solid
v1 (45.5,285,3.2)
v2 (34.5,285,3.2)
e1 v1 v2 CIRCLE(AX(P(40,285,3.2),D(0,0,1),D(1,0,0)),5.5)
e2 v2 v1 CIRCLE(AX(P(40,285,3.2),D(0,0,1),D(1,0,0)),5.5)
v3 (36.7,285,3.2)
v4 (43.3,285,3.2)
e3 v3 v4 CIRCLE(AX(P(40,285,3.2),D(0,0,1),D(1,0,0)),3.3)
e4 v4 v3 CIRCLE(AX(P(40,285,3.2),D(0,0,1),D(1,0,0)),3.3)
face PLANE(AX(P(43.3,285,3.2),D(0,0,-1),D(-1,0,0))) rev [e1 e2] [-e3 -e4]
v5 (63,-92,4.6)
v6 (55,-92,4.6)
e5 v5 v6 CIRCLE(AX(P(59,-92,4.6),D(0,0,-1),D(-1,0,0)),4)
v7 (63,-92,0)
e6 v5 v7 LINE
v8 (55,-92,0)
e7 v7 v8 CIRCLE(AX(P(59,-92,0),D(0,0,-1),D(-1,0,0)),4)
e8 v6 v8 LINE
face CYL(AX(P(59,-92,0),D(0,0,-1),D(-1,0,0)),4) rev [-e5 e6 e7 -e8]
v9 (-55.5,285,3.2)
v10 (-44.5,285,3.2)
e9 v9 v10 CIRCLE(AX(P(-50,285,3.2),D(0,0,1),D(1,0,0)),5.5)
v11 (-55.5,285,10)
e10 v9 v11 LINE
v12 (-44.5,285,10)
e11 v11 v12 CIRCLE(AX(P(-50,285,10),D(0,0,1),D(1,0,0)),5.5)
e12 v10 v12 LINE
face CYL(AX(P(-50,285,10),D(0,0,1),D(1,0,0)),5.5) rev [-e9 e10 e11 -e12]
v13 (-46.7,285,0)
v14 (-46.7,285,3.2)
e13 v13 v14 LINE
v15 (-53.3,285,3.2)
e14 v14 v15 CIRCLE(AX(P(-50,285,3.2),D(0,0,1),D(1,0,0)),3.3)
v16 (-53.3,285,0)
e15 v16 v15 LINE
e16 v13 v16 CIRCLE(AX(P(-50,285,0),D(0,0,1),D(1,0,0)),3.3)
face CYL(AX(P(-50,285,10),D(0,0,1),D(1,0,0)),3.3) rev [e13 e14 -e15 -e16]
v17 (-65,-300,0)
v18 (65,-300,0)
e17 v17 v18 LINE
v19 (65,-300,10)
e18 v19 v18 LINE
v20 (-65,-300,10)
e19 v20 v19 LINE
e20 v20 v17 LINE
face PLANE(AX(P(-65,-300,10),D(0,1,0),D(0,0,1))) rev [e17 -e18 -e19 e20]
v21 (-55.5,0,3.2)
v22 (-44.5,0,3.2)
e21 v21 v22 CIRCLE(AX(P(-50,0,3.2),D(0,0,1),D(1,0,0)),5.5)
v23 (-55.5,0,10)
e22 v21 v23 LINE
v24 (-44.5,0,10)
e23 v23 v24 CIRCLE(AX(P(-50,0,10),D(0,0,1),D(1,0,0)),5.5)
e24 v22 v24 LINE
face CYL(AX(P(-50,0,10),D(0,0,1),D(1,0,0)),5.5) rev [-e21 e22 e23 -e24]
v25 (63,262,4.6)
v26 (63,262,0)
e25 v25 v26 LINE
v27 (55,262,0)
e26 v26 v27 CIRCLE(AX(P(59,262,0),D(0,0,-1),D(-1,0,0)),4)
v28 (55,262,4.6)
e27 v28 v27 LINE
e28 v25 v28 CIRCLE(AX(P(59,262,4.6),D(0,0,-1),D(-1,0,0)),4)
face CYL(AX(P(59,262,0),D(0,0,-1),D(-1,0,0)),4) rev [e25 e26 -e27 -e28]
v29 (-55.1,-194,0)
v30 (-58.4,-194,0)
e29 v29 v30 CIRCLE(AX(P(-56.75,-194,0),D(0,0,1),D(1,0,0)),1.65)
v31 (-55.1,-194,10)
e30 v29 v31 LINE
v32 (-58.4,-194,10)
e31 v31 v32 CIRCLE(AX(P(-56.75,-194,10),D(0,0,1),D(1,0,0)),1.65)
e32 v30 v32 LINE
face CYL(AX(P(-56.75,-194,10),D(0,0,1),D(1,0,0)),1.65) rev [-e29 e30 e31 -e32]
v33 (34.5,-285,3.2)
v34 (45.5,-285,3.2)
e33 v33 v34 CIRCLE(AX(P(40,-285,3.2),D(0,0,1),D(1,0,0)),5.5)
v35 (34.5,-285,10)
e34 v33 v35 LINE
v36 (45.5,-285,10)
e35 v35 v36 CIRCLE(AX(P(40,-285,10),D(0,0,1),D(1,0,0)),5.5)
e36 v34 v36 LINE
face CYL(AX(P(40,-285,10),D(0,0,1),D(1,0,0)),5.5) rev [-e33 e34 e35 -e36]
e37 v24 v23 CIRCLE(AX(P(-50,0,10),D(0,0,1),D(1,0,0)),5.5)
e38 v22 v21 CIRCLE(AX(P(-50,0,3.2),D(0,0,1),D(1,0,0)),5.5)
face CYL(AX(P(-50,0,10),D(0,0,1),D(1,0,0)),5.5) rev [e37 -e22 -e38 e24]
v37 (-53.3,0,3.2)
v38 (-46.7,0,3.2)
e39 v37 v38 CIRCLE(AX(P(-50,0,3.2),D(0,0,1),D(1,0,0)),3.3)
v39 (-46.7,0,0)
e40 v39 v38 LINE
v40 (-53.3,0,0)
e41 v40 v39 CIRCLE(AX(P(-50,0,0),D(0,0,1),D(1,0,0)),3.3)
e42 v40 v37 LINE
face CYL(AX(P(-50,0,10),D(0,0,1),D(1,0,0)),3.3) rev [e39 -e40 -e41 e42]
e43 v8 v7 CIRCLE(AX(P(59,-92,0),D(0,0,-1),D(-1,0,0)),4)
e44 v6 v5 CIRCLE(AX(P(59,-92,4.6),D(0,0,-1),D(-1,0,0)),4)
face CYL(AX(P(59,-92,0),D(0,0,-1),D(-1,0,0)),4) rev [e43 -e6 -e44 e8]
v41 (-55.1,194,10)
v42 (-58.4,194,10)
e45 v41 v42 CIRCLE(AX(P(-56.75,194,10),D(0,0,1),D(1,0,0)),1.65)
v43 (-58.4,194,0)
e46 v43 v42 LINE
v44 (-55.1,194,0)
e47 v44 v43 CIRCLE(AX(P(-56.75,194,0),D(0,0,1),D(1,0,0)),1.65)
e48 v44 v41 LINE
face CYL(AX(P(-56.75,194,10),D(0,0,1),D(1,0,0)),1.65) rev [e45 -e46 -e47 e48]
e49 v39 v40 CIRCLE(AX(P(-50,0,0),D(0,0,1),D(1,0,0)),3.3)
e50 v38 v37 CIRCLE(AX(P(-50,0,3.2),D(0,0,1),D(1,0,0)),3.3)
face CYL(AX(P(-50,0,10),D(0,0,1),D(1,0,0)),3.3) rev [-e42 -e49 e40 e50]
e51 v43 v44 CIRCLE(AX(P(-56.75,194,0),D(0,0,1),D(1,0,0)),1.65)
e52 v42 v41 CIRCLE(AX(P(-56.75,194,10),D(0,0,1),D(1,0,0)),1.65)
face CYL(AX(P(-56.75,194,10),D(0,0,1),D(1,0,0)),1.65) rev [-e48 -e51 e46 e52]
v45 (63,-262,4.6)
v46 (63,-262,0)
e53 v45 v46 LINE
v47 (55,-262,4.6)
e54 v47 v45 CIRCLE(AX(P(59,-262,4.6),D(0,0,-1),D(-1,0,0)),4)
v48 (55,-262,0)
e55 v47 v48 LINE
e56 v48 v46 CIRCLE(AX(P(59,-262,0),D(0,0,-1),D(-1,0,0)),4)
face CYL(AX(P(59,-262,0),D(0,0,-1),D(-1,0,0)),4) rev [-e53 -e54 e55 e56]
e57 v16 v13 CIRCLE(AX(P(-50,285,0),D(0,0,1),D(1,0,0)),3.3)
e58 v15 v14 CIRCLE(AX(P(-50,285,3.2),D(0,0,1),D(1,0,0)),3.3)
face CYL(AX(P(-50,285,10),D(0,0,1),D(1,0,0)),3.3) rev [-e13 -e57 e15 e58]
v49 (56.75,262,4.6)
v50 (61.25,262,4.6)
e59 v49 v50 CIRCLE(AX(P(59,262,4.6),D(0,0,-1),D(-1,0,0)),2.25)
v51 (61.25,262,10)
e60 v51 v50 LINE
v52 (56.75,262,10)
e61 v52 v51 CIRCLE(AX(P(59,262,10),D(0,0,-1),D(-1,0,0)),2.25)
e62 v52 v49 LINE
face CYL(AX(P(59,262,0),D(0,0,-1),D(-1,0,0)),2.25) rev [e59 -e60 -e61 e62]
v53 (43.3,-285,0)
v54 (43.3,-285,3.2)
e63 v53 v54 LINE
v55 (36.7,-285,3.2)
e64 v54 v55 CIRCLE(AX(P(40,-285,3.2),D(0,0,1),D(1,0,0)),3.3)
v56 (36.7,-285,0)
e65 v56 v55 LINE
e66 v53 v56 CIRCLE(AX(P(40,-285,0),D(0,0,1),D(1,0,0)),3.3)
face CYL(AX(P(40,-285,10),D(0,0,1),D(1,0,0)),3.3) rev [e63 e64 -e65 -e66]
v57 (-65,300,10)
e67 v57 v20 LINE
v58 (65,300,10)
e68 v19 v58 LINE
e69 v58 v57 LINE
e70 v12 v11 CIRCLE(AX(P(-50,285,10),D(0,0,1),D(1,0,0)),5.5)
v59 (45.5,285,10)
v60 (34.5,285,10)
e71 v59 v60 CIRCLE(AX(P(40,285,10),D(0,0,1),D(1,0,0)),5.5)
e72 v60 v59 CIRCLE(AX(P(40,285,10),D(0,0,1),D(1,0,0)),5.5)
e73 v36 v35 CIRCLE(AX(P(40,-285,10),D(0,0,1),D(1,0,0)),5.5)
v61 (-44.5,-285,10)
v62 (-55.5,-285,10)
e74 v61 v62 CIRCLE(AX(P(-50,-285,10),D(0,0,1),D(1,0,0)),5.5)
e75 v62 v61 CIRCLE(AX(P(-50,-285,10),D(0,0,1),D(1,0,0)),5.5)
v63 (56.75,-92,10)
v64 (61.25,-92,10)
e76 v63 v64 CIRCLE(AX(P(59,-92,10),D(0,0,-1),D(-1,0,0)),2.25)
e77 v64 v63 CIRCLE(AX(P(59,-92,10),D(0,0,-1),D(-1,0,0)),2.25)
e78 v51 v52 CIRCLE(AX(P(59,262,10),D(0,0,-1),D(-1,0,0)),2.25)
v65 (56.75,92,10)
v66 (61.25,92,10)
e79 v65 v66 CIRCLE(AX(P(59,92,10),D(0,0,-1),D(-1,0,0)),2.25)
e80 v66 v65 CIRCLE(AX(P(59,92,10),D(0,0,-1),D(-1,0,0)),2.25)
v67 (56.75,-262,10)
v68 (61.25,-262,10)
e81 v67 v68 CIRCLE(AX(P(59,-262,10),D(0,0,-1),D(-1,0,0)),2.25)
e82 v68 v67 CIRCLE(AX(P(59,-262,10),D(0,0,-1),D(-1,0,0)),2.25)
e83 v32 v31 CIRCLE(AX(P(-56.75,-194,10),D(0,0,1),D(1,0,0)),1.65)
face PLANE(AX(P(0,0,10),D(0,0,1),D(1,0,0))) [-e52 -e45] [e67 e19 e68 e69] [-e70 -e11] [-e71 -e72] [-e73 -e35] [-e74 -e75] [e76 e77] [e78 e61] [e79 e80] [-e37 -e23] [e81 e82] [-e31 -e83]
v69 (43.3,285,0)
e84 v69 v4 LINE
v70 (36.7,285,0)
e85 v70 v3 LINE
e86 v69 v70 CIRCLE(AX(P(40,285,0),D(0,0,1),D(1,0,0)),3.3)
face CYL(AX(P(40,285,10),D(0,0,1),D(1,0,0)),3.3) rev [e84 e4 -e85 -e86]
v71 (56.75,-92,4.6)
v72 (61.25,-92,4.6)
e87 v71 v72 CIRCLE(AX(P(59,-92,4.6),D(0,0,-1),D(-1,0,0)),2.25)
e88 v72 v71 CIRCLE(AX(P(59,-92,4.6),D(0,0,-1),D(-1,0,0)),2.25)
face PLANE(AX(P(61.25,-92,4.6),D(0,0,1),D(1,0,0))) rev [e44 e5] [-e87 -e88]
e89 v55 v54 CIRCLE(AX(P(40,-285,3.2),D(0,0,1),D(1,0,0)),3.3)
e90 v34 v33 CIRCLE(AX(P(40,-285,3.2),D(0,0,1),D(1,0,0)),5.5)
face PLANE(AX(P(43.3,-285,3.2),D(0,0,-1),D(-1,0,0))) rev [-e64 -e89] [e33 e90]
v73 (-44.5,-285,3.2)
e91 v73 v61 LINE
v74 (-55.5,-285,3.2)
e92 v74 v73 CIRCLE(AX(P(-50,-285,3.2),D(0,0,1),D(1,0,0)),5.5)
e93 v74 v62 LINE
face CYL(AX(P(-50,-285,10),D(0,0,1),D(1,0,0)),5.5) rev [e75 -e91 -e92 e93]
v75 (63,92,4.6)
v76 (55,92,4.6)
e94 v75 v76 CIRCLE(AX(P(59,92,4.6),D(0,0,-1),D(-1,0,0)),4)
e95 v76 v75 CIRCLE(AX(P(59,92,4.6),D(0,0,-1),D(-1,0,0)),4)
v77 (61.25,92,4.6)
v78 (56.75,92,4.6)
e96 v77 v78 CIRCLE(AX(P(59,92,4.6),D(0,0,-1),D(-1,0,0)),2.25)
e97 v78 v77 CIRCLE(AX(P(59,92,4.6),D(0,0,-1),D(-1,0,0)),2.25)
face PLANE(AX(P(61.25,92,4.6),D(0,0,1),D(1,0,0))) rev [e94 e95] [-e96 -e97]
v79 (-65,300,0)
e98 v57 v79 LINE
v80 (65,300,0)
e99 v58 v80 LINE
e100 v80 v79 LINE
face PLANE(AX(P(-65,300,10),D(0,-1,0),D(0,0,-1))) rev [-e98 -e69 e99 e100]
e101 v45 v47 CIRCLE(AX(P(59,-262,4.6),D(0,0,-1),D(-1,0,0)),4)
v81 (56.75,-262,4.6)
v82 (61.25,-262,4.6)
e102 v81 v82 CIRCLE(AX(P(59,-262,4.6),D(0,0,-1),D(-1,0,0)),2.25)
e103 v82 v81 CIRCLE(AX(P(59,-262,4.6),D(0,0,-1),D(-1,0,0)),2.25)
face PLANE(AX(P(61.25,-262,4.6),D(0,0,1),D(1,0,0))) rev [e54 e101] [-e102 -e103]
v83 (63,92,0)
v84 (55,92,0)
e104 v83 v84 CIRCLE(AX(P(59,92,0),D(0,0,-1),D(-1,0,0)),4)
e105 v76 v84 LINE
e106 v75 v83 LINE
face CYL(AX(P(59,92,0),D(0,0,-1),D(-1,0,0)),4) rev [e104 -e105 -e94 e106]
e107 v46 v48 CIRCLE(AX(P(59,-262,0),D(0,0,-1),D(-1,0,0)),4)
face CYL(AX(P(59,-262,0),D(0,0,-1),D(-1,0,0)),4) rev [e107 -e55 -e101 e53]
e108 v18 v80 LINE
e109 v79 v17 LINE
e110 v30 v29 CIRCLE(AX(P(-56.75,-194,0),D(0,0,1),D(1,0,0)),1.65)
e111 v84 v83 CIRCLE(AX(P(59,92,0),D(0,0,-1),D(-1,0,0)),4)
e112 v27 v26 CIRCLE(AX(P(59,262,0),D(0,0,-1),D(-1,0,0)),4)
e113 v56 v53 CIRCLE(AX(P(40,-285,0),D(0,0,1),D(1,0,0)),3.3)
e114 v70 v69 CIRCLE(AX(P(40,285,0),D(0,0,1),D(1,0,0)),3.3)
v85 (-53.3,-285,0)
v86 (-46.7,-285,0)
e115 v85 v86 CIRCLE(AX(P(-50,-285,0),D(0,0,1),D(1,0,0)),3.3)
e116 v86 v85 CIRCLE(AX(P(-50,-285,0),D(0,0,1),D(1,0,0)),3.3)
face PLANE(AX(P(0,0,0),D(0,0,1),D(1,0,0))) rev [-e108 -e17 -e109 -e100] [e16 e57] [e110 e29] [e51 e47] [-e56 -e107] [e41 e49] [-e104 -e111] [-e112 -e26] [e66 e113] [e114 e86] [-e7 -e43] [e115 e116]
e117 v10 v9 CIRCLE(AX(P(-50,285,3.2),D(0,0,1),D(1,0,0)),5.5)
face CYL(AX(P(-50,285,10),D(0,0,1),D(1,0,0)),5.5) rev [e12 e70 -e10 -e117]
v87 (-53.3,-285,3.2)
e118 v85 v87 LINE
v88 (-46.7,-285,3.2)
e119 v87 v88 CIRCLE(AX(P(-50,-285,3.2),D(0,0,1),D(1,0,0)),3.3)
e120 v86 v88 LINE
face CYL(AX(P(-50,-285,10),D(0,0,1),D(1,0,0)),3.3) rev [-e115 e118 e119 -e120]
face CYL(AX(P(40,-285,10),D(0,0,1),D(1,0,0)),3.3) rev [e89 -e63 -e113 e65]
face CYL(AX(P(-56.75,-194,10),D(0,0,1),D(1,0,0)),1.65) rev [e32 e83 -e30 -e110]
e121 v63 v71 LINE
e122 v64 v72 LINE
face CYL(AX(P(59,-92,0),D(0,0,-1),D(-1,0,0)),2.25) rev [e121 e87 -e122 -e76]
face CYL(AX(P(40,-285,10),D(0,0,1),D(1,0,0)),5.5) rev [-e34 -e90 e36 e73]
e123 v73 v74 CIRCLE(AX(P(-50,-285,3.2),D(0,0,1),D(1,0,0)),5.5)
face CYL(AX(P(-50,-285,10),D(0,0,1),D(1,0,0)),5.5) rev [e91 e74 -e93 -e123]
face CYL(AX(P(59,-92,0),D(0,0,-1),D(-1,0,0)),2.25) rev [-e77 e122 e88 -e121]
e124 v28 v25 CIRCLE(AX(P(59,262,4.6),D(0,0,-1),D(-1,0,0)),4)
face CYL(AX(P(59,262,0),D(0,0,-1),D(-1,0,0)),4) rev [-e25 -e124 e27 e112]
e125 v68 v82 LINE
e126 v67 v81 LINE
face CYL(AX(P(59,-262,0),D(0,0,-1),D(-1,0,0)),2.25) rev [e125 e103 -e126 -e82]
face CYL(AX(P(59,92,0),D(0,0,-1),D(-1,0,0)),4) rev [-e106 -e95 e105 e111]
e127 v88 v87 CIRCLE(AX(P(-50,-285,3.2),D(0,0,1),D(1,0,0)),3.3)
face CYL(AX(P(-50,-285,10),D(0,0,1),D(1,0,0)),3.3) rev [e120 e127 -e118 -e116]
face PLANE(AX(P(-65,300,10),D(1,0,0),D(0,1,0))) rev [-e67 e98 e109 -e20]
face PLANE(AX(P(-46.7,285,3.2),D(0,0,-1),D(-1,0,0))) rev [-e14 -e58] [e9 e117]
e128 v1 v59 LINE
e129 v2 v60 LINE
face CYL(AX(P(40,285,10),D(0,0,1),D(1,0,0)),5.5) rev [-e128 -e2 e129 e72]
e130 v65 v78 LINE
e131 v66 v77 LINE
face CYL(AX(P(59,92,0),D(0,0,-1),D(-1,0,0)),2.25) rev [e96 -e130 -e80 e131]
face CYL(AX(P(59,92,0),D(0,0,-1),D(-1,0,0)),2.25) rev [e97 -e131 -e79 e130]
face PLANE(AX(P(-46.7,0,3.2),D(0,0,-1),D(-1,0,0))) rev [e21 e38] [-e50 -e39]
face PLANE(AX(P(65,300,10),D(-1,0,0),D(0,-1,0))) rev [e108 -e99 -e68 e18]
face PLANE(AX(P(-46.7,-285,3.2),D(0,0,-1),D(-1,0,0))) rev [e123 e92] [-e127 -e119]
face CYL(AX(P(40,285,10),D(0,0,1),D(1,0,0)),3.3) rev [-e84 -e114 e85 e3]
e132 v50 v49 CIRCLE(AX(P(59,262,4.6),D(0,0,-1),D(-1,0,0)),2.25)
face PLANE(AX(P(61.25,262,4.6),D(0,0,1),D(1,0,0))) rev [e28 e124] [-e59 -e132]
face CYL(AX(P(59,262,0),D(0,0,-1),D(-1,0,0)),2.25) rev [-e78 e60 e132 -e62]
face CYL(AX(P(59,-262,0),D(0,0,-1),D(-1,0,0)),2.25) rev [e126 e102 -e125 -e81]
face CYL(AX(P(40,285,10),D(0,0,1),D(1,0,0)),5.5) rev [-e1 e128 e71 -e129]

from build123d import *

# Parameters (mm, degrees)
SKETCH_1_W                  = 130
SKETCH_1_H                  = 600
EXTRUDE_1_DEPTH             = 10
HOLE_WIZARD_2_D             = 6.6
HOLE_WIZARD_2_CBORE_D       = 11
HOLE_WIZARD_2_CBORE_DEPTH   = 6.8
HOLE_WIZARD_M4_2_D          = 3.3
HOLE_WIZARD_2_2_D           = 4.5
HOLE_WIZARD_2_2_CBORE_D     = 8
HOLE_WIZARD_2_2_CBORE_DEPTH = 4.6


with BuildPart() as part:
    # 草图1 → 凸台-拉伸1 (new body)
    with BuildSketch(Plane.XY):
        Rectangle(SKETCH_1_W, SKETCH_1_H)
    extrude(amount=EXTRUDE_1_DEPTH)

    # Hole Wizard 2 (through all)
    with Locations(Plane.XY.offset(10)):
        with Locations((-50, 285), (-50, 0), (-50, -285), (40, 285), (40, -285)):
            CounterBoreHole(HOLE_WIZARD_2_D / 2, HOLE_WIZARD_2_CBORE_D / 2, HOLE_WIZARD_2_CBORE_DEPTH)

    # M4 螺纹孔2 (through all)
    with Locations(Plane.XY.offset(10)):
        with Locations((-56.75, 194), (-56.75, -194)):
            Hole(HOLE_WIZARD_M4_2_D / 2)

    # Hole Wizard 2 2 (through all)
    with Locations(Plane(origin=(0, 0, 0), x_dir=(-1, 0, 0), z_dir=(0, 0, -1))):
        with Locations((-59, -262), (-59, -92), (-59, 92), (-59, 262)):
            CounterBoreHole(HOLE_WIZARD_2_2_D / 2, HOLE_WIZARD_2_2_CBORE_D / 2, HOLE_WIZARD_2_2_CBORE_DEPTH)


solid = part.part
